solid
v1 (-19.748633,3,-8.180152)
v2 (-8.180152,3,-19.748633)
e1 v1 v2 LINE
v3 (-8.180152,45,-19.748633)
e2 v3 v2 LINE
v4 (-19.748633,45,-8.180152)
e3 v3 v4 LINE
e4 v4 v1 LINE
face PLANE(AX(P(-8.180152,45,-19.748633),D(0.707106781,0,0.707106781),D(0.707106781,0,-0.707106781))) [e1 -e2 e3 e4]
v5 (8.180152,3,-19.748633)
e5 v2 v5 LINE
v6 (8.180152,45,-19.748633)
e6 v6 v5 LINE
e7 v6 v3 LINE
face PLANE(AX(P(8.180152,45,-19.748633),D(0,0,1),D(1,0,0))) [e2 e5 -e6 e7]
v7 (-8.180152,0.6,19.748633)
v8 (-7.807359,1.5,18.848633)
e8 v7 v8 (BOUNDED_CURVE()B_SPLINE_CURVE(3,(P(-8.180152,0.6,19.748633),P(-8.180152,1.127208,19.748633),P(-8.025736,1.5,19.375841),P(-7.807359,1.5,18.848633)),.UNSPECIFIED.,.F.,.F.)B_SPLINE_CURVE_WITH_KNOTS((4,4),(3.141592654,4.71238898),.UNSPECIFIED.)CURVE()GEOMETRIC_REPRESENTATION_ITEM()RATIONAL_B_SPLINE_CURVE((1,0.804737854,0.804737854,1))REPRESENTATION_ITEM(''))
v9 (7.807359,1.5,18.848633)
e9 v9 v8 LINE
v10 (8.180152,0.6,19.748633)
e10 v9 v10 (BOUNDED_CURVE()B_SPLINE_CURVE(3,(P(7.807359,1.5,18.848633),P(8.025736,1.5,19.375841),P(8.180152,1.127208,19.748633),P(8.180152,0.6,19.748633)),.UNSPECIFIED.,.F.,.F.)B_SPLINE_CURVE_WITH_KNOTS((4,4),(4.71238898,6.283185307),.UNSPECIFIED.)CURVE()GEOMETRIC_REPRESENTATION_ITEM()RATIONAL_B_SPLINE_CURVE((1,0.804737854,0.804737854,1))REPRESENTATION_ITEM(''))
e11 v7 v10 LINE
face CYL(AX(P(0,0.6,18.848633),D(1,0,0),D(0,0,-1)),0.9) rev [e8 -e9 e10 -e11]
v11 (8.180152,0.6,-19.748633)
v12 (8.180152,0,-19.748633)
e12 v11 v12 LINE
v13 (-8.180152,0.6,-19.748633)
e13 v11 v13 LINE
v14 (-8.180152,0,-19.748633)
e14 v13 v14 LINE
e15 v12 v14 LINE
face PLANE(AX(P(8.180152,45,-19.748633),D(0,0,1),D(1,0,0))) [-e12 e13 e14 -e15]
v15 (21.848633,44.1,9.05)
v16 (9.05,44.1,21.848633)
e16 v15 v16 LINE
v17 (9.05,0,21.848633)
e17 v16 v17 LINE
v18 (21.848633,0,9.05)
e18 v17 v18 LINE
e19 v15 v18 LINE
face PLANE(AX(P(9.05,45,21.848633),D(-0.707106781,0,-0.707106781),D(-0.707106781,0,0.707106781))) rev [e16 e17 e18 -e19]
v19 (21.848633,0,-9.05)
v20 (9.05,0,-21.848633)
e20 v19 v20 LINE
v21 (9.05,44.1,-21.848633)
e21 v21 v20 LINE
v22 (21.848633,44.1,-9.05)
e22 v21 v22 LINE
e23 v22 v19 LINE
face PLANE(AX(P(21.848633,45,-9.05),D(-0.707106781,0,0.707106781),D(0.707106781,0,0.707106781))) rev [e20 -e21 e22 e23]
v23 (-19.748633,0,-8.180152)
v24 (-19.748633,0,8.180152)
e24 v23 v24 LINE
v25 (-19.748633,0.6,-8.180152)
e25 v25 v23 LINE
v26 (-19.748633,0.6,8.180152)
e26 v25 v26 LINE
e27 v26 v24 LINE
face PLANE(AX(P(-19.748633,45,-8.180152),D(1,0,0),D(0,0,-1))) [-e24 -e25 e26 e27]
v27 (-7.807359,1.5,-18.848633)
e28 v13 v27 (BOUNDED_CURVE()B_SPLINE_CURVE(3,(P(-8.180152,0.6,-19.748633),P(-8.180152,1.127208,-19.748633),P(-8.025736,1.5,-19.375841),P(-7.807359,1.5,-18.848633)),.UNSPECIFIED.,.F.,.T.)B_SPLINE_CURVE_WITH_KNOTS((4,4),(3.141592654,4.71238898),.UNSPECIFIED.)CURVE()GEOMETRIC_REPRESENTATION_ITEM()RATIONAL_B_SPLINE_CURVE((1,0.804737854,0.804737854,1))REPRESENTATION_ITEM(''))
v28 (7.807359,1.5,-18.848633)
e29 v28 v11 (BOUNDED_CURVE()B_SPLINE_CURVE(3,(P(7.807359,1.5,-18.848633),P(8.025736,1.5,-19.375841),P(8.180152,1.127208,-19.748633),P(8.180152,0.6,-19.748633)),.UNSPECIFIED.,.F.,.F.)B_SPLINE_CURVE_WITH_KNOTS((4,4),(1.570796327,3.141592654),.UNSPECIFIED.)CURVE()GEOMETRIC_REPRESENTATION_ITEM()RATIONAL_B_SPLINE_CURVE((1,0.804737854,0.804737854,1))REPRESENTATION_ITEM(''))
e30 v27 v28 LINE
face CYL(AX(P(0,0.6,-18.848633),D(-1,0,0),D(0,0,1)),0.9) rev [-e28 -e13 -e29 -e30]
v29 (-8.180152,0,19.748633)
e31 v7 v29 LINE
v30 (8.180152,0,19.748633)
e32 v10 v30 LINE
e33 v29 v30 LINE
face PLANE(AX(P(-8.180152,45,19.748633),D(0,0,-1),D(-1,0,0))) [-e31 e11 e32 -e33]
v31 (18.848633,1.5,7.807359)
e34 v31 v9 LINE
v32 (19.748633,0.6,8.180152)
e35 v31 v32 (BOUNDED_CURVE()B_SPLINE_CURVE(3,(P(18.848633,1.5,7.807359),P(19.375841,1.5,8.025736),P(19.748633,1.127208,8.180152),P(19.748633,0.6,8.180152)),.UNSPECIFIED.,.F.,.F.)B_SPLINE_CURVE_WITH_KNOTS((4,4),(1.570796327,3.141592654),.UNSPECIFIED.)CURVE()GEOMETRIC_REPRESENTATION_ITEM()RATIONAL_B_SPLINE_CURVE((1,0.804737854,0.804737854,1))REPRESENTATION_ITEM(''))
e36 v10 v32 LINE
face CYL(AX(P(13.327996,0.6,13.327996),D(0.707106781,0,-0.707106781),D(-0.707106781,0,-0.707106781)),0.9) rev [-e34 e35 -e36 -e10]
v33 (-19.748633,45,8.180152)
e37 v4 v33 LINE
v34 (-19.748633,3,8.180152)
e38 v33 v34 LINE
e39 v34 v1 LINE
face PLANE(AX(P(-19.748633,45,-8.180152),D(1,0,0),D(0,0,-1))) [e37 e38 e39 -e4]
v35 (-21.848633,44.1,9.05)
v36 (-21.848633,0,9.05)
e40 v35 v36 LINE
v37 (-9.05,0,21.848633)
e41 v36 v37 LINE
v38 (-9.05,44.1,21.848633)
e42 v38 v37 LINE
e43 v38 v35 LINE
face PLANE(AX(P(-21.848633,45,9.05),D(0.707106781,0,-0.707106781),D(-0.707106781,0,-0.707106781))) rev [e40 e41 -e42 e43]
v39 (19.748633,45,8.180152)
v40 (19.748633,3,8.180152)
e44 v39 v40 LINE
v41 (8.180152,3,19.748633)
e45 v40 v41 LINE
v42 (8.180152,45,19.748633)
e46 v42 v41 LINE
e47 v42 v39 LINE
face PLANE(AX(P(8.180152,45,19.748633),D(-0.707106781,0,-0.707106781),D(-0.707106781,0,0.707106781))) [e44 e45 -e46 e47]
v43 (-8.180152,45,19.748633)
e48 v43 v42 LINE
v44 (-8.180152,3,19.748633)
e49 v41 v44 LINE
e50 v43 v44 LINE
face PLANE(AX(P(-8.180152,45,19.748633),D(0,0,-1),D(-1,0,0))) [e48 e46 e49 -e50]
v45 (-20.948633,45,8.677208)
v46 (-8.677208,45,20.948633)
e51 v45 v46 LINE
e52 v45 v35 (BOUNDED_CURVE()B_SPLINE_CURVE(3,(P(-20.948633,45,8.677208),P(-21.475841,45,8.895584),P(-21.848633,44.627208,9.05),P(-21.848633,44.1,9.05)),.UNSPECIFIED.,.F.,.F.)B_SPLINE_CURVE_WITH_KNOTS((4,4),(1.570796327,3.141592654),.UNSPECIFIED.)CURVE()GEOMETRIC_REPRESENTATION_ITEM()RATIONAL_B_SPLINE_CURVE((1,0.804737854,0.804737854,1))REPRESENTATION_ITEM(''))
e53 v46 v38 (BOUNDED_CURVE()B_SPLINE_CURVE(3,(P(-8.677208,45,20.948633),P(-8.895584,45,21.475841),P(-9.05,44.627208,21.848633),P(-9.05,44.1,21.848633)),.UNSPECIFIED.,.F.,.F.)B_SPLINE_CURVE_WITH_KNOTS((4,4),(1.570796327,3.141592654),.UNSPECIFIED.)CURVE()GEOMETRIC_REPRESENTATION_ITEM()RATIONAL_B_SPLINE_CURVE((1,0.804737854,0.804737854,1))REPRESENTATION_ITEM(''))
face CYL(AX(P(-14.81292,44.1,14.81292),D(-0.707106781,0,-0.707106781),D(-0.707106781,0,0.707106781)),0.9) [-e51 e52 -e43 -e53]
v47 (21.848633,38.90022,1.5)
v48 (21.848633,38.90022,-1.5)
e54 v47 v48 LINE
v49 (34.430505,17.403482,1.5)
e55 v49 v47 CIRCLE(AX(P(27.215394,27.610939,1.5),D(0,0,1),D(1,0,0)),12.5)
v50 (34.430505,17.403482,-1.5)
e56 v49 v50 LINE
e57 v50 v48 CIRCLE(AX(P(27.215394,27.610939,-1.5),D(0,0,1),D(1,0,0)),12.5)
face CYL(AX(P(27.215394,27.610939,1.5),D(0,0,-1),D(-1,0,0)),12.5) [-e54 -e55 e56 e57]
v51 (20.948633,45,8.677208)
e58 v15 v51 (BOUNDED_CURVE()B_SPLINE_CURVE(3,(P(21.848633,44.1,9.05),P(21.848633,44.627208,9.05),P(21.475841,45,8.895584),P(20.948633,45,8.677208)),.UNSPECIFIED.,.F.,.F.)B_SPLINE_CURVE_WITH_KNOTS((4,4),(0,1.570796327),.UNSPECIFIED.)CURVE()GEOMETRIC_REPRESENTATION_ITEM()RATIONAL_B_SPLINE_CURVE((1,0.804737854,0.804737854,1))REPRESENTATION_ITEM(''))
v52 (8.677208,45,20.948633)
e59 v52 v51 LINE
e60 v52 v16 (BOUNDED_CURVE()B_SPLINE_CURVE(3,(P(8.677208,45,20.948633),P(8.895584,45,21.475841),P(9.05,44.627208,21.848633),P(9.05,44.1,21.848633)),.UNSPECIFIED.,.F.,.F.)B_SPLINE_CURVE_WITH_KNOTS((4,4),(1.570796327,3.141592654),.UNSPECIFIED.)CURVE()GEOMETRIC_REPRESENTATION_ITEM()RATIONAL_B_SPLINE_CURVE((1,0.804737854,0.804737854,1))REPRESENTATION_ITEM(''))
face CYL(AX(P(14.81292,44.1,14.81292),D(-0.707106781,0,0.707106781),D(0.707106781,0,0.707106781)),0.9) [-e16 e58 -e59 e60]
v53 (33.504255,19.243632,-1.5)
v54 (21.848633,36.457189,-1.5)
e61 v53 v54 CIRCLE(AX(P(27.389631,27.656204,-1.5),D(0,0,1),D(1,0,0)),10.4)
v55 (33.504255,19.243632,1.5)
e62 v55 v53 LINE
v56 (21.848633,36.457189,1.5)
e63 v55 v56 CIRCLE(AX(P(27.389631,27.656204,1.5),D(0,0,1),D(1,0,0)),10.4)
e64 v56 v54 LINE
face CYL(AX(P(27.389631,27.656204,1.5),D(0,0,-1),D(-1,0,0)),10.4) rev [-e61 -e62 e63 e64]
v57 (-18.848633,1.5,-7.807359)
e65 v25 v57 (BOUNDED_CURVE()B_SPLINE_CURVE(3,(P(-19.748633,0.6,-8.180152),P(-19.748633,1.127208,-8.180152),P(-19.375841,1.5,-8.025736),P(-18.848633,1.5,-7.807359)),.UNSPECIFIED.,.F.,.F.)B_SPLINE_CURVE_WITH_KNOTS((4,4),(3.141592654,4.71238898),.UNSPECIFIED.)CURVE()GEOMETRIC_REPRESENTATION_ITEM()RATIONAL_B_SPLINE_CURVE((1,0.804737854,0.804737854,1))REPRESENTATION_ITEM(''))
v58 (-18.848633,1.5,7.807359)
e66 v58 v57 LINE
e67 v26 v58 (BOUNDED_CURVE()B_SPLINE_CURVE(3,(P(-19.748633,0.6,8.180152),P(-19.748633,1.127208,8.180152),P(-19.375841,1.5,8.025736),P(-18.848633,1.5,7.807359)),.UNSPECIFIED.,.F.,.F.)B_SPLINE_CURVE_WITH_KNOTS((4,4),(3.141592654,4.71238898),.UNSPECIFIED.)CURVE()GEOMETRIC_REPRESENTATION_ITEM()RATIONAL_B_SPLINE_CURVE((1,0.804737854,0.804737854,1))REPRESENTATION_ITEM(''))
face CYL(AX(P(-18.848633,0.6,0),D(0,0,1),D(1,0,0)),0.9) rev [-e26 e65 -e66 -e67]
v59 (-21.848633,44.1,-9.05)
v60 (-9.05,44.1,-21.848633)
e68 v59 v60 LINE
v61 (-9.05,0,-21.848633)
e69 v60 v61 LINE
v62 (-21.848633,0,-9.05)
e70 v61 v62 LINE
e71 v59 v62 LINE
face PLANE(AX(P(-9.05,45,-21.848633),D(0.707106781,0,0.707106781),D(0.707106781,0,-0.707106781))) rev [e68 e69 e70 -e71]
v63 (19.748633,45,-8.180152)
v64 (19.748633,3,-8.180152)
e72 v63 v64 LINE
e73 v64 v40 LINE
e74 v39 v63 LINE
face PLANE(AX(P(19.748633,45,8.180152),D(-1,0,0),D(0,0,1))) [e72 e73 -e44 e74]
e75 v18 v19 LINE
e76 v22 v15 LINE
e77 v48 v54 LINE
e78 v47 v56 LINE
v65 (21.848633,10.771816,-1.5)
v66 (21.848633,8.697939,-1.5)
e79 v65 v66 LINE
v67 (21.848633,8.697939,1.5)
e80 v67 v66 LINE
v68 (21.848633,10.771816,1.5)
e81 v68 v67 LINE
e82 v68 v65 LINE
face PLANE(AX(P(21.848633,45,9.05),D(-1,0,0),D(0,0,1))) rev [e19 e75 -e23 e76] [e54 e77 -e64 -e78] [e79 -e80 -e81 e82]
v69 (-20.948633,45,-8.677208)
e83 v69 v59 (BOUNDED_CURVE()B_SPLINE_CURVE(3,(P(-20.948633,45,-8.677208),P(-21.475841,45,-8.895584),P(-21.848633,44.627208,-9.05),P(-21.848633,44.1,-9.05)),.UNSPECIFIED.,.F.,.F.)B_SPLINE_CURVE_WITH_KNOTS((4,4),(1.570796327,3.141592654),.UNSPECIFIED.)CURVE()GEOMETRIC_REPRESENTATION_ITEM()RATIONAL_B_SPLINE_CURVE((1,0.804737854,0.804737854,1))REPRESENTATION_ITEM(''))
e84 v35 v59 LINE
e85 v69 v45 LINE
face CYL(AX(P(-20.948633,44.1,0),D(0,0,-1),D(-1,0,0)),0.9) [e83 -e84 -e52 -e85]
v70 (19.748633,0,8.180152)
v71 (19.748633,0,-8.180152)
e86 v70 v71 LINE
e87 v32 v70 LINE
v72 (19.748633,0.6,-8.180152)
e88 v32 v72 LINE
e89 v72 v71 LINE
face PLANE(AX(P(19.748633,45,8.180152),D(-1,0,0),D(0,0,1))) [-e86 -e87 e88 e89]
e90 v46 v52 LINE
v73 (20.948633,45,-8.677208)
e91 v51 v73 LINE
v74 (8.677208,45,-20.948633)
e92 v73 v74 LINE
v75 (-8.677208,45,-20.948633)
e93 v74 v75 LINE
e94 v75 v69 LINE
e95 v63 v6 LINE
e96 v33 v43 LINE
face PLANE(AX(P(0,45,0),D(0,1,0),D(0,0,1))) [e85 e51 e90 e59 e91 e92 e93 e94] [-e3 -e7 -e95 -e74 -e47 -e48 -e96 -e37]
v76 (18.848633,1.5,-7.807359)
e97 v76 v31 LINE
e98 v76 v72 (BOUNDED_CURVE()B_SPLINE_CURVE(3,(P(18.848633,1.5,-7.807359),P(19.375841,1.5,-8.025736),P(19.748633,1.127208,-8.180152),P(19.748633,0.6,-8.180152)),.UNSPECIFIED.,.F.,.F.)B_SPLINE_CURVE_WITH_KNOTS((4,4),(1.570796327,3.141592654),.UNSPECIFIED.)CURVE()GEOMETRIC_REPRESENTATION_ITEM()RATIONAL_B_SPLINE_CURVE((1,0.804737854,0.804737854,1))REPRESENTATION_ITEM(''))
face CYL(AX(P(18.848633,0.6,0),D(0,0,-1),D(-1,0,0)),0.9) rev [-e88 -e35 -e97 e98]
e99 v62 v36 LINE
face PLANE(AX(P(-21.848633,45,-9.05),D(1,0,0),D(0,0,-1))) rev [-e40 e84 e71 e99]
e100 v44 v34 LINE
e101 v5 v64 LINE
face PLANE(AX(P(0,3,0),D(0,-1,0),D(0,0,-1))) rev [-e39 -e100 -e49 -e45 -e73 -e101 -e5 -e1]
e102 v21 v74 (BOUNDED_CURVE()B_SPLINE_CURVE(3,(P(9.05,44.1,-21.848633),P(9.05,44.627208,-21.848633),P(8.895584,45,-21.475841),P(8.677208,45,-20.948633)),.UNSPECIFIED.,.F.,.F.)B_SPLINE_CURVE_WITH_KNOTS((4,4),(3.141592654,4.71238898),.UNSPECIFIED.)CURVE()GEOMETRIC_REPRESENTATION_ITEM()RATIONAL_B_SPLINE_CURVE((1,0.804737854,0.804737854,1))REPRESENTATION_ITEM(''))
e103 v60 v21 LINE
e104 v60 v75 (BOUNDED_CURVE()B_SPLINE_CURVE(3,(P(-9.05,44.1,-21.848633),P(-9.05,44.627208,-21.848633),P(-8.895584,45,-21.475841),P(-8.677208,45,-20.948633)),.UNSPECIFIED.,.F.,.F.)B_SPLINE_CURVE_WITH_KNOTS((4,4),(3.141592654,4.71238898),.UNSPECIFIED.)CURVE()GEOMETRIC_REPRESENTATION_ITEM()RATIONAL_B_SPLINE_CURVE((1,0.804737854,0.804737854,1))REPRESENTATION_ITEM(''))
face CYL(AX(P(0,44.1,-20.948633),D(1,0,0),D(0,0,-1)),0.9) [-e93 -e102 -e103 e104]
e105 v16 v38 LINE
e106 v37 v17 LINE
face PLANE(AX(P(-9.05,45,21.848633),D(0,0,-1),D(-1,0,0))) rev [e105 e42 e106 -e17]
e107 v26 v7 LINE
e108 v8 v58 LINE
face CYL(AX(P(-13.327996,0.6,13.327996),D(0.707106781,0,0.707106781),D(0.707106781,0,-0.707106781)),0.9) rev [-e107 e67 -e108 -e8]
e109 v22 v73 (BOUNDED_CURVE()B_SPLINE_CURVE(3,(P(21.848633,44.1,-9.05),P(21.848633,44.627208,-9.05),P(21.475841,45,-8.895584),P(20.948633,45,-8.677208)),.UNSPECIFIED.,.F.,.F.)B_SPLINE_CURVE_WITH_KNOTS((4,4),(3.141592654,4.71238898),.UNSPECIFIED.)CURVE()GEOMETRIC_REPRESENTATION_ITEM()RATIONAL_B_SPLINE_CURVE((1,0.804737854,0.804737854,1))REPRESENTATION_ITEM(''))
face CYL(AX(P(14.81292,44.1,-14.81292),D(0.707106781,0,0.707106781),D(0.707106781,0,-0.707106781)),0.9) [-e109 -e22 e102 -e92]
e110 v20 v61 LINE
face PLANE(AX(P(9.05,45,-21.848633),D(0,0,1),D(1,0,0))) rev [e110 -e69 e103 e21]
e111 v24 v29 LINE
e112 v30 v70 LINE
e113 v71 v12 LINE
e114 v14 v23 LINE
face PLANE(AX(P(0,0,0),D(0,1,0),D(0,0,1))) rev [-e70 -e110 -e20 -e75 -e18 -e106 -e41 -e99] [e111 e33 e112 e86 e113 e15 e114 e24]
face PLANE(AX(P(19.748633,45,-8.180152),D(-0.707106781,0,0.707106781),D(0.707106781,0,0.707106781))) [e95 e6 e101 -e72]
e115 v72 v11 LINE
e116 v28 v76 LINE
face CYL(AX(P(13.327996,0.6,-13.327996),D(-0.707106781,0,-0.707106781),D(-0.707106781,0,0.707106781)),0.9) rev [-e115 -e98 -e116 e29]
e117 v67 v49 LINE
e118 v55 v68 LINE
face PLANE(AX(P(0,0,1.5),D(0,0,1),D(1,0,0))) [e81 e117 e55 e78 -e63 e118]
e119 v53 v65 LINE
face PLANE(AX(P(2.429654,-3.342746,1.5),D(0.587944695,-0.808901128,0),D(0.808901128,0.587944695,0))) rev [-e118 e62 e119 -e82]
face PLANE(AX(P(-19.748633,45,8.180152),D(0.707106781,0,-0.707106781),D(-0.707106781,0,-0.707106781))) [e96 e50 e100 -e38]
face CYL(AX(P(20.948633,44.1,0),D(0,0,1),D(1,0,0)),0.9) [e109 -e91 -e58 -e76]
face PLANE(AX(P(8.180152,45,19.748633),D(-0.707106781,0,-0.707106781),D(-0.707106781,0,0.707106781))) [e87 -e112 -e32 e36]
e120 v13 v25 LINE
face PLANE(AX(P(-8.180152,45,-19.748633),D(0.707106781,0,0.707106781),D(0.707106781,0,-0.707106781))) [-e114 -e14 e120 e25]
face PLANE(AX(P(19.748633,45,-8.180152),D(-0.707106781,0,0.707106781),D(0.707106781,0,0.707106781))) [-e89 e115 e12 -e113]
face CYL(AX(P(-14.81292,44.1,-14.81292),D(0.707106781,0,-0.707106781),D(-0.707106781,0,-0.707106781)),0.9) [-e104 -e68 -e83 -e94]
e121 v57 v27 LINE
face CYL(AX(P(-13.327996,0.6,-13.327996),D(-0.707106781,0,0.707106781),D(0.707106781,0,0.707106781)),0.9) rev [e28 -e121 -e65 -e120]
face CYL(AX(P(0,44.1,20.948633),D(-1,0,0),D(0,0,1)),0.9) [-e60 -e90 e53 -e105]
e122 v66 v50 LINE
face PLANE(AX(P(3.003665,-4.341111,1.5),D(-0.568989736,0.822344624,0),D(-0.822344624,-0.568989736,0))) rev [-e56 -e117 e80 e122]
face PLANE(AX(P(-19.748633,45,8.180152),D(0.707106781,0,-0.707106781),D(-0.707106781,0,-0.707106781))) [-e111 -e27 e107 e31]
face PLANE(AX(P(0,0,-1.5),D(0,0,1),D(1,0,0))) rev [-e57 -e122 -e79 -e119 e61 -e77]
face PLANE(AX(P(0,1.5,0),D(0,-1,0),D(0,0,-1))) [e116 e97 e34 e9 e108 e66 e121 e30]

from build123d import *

# Parameters (mm, degrees)
OCTAGON_WALL_45MM_DEPTH    = 45
BOTTOM_START               = -3
BOTTOM_PLATE_1_5MM_DEPTH   = 1.5
BOTTOM_PLATE_FILLET_R0_9_R = 0.9
HANDLE_3MM_DEPTH           = 1.5
WALL_EDGE_FILLET_R0_9_R    = 0.9


with BuildPart() as part:
    # Octagon Wall Profile → Octagon Wall 45mm (new body)
    with BuildSketch(Plane(origin=(0, 0, 0), x_dir=(1, 0, 0), z_dir=(0, 1, 0))):
        Polygon((21.848632739, -9.05), (21.848632739, 9.05), (9.05, 21.848632739), (-9.05, 21.848632739), (-21.848632739, 9.05), (-21.848632739, -9.05), (-9.05, -21.848632739), (9.05, -21.848632739), align=None)
        Polygon((-19.748632739, 8.180151519), (-19.748632739, -8.180151519), (-8.180151519, -19.748632739), (8.180151519, -19.748632739), (19.748632739, -8.180151519), (19.748632739, 8.180151519), (8.180151519, 19.748632739), (-8.180151519, 19.748632739), align=None, mode=Mode.SUBTRACT)
    extrude(amount=OCTAGON_WALL_45MM_DEPTH)

    # Bottom Plate Profile → Bottom Plate 1.5mm (add)
    with BuildSketch(Plane.XZ.offset(BOTTOM_START)):
        Polygon((19.748632739, -8.180151519), (19.748632739, 8.180151519), (8.180151519, 19.748632739), (-8.180151519, 19.748632739), (-19.748632739, 8.180151519), (-19.748632739, -8.180151519), (-8.180151519, -19.748632739), (8.180151519, -19.748632739), align=None)
    extrude(amount=BOTTOM_PLATE_1_5MM_DEPTH)

    # Bottom Plate Fillet R0.9
    bottom_plate_fillet_r0_9_edges = [part.edges().sort_by_distance(p)[0] for p in [
        (13.964392129, 1.5, -13.964392129),
        (19.748632739, 1.5, 0),
        (13.964392129, 1.5, 13.964392129),
        (0, 1.5, 19.748632739),
        (-13.964392129, 1.5, 13.964392129),
        (-19.748632739, 1.5, 0),
        (-13.964392129, 1.5, -13.964392129),
        (0, 1.5, -19.748632739),
    ]]
    fillet(bottom_plate_fillet_r0_9_edges, radius=BOTTOM_PLATE_FILLET_R0_9_R)

    # Handle Profile → Handle 3mm (add, symmetric)
    with BuildSketch(Plane.XY):
        with BuildLine():
            ThreePointArc((34.430505485, 17.403482342), (38.003421513, 33.925087018), (21.848632739, 38.90022015))
            Line((21.848632739, 38.90022015), (21.848632739, 36.457189456))
            ThreePointArc((21.848632739, 36.457189456), (36.001186663, 33.487250387), (33.504255362, 19.243632352))
            Line((33.504255362, 19.243632352), (21.848632739, 10.771816388))
            Line((21.848632739, 10.771816388), (21.848632739, 8.697939383))
            Line((21.848632739, 8.697939383), (34.430505485, 17.403482342))
        make_face()
    extrude(amount=HANDLE_3MM_DEPTH, both=True)

    # Wall Edge Fillet R0.9
    wall_edge_fillet_r0_9_edges = [part.edges().sort_by_distance(p)[0] for p in [
        (15.44931637, 45, -15.44931637),
        (0, 45, -21.848632739),
        (-15.44931637, 45, -15.44931637),
        (-21.848632739, 45, 0),
        (-15.44931637, 45, 15.44931637),
        (0, 45, 21.848632739),
        (15.44931637, 45, 15.44931637),
        (21.848632739, 45, 0),
    ]]
    fillet(wall_edge_fillet_r0_9_edges, radius=WALL_EDGE_FILLET_R0_9_R)


solid = part.part
